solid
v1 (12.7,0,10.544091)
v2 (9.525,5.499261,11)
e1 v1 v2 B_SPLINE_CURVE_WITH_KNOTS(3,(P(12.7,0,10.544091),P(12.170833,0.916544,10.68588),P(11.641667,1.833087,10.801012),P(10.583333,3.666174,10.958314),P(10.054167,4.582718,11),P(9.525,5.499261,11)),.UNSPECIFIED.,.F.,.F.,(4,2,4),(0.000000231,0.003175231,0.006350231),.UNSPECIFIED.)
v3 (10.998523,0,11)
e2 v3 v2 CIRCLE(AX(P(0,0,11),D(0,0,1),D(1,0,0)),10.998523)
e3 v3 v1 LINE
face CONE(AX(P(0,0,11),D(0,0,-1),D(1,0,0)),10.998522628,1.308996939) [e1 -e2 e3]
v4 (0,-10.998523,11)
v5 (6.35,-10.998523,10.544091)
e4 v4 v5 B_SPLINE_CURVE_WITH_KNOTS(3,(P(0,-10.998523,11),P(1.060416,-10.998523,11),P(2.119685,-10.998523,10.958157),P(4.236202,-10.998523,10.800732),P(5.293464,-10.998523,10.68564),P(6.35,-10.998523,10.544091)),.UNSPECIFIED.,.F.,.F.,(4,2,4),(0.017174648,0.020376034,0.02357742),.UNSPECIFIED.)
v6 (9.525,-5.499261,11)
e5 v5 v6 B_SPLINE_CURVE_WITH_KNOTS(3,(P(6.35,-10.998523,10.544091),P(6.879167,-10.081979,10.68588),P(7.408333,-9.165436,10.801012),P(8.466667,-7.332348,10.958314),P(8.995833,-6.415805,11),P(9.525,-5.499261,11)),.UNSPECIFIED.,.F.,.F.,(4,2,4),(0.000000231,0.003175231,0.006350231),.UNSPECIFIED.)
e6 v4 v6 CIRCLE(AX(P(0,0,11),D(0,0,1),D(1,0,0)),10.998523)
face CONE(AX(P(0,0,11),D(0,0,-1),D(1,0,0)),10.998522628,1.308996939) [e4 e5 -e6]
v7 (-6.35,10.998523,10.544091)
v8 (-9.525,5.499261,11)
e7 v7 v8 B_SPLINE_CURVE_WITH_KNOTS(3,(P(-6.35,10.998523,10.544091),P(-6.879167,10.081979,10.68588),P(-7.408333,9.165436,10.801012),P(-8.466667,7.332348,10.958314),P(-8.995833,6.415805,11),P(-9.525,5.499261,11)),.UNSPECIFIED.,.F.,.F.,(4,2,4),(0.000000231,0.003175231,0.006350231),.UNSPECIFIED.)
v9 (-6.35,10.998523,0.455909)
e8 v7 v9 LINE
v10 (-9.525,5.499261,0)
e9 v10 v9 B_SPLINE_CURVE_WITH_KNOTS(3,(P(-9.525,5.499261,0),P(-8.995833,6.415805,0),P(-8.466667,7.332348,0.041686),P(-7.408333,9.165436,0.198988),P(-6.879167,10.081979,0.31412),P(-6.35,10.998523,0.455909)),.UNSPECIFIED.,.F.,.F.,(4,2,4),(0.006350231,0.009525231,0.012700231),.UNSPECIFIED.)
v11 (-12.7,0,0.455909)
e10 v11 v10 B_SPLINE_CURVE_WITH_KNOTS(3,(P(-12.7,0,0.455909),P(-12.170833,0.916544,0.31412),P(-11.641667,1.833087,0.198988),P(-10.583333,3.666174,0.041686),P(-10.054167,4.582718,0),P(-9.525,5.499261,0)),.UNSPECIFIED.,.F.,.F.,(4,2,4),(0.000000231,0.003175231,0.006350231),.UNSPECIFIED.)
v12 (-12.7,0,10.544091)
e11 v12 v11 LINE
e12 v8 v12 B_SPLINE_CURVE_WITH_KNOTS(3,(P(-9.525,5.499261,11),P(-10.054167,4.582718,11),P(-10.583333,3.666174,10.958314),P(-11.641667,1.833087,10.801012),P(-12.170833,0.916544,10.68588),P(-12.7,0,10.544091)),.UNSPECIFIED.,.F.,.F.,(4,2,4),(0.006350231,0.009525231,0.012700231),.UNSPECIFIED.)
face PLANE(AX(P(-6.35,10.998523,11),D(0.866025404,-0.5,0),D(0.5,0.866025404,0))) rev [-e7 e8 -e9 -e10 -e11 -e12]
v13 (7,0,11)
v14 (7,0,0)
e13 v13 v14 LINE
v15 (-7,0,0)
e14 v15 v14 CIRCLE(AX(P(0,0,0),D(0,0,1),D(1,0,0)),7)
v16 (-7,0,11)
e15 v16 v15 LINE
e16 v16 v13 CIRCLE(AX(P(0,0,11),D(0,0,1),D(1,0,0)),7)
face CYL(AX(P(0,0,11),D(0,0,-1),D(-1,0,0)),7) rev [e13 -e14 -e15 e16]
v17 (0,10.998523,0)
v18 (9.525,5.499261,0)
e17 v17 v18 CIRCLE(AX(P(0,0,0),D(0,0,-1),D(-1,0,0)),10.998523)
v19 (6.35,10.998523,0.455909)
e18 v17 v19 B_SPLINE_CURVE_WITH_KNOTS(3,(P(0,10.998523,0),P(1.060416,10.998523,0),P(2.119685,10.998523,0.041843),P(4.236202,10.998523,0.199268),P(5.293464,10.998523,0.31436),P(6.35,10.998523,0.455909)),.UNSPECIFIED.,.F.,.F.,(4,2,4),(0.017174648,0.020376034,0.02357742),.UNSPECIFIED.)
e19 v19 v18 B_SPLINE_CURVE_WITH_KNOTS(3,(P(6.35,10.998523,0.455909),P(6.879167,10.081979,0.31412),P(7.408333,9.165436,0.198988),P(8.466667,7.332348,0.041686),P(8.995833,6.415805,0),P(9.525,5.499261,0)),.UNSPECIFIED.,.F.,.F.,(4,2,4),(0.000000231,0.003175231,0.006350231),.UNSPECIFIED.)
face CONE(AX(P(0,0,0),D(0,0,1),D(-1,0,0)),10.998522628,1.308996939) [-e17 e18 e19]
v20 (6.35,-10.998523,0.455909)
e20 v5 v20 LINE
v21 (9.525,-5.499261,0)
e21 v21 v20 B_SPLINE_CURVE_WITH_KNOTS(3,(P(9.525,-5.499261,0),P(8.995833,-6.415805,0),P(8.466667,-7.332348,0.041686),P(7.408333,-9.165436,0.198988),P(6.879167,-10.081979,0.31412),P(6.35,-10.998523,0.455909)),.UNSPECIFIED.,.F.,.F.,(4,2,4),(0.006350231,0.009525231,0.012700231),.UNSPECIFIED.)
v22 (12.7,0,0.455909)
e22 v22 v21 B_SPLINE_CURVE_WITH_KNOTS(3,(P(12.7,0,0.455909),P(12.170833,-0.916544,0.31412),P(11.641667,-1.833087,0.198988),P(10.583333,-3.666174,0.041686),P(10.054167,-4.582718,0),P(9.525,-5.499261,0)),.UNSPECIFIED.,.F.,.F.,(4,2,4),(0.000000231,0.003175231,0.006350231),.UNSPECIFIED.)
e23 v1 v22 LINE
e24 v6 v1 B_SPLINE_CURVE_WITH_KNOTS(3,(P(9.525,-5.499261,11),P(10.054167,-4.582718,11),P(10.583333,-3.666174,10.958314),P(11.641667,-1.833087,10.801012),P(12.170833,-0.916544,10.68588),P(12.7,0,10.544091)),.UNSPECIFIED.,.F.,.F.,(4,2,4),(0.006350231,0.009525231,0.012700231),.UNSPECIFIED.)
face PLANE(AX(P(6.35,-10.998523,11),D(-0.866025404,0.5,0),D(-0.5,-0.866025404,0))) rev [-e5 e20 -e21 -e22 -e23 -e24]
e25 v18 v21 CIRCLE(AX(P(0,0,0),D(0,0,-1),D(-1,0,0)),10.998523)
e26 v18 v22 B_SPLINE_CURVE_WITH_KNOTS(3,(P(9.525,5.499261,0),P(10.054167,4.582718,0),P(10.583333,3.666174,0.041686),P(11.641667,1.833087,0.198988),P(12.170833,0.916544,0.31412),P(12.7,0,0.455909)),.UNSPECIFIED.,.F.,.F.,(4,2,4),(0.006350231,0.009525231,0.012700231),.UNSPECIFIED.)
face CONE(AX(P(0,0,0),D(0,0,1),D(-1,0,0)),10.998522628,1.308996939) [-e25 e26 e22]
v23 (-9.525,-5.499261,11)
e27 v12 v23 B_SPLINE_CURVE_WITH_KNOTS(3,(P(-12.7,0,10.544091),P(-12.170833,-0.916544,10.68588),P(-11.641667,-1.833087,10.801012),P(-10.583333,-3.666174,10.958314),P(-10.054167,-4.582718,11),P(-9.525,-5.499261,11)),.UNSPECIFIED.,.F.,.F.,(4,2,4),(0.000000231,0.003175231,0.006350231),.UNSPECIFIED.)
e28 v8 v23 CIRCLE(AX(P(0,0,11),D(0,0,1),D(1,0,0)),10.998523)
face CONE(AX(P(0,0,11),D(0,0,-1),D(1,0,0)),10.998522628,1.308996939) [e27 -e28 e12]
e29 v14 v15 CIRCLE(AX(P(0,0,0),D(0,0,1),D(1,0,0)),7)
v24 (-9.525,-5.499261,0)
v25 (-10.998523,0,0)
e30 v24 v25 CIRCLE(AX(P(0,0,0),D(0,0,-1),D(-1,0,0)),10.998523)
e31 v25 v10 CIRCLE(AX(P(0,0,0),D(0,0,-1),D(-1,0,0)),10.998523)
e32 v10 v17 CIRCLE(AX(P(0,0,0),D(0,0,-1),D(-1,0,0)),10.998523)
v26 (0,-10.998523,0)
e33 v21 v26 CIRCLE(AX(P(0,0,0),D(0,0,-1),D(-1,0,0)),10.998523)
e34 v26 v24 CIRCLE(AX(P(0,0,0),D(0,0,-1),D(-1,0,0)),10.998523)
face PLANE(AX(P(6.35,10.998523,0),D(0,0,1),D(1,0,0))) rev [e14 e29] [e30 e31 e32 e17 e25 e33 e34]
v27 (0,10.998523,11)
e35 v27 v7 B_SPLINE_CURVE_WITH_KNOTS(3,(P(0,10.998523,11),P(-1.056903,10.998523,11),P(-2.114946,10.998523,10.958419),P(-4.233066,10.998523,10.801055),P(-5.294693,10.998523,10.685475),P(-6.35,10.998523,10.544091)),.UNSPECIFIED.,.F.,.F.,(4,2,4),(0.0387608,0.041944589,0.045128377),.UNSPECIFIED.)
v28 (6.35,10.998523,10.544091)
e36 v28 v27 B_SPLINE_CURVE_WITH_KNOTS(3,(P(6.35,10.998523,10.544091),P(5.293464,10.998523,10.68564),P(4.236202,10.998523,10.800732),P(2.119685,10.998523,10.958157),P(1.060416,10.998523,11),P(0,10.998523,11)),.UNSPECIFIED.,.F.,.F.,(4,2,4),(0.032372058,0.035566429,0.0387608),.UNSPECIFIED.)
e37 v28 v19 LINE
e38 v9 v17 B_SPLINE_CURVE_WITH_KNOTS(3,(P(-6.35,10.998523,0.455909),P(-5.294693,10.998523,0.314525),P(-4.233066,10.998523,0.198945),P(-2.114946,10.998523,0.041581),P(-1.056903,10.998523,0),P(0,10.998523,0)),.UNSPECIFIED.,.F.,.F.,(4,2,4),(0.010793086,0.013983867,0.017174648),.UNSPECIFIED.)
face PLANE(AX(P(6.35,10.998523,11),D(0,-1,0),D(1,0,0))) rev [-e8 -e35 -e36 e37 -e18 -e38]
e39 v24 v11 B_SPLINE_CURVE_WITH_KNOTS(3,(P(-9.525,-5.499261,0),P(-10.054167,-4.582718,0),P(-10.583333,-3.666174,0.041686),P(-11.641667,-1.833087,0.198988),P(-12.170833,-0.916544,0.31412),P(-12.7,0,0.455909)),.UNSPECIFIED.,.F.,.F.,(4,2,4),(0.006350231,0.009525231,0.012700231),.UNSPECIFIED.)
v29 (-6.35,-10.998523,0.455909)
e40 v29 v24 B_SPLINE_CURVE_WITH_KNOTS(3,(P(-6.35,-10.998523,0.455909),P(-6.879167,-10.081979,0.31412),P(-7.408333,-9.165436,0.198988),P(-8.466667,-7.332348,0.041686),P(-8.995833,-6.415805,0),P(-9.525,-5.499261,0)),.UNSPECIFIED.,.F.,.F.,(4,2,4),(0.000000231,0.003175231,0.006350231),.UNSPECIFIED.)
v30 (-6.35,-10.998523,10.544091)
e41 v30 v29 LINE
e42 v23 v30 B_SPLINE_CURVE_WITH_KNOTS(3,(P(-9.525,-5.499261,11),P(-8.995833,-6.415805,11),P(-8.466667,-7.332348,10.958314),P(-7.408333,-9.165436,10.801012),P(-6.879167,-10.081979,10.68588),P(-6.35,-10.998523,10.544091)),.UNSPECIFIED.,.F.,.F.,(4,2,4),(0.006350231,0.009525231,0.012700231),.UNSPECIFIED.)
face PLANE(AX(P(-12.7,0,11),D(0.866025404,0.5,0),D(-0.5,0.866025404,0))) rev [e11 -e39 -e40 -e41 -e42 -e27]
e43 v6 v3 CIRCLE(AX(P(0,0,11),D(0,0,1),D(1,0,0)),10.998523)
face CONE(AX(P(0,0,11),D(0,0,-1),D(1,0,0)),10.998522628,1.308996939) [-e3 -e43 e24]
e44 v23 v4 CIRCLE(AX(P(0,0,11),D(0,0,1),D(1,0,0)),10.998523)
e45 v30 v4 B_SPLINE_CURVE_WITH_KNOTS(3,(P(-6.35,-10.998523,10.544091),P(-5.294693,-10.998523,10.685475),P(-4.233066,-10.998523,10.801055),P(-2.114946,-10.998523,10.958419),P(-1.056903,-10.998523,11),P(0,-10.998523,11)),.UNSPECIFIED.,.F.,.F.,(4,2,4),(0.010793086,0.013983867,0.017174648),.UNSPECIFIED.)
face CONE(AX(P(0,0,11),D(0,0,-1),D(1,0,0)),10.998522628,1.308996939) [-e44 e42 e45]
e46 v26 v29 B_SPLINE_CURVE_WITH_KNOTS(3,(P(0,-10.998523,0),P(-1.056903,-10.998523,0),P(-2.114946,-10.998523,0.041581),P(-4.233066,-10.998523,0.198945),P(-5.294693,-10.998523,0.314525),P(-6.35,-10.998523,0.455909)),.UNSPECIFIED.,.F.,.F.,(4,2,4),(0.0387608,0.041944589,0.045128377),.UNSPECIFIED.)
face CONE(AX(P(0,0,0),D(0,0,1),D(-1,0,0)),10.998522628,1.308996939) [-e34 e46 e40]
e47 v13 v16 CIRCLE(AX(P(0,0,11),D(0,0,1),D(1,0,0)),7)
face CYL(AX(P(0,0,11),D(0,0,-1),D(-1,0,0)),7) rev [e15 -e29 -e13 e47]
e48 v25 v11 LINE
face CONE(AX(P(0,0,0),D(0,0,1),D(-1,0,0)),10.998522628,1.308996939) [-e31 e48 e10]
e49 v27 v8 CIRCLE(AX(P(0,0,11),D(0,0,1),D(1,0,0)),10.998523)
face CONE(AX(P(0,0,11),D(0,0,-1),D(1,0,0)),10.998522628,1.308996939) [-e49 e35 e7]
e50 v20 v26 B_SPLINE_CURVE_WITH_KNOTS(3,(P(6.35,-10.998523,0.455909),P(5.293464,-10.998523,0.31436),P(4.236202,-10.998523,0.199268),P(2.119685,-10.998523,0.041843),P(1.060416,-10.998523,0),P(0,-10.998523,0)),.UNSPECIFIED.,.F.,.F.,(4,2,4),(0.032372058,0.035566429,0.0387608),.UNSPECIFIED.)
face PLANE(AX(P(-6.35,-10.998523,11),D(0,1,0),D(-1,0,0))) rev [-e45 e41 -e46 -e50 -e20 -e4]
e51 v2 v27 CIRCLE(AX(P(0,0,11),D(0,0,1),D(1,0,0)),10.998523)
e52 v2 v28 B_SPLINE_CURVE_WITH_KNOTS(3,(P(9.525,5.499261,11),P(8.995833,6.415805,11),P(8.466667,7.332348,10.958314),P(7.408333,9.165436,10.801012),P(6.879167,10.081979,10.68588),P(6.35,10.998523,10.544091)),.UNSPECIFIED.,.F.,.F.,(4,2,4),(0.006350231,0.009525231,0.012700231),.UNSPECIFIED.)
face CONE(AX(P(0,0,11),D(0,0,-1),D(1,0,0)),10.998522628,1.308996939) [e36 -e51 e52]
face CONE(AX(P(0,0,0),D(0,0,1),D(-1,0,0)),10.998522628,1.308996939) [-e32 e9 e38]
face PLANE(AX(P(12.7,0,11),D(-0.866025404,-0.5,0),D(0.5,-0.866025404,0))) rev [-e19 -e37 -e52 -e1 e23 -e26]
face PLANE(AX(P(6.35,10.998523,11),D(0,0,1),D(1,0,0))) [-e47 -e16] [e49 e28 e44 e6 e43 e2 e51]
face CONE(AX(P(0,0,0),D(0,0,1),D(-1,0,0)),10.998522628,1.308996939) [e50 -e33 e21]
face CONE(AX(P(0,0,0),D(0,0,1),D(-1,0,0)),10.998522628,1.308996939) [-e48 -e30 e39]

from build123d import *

# Parameters (mm, degrees)
SKETCH1_R          = 7
BASE_EXTRUDE_DEPTH = 11
SKETCH2_OUTSIDE_W  = 318.108
SKETCH2_OUTSIDE_H  = 314.706
SKETCH2_OUTSIDE_R  = 10.998522628
CUT_EXTRUDE1_DEPTH = 38
CUT_EXTRUDE1_DRAFT = -75
SKETCH3_OUTSIDE_W  = 318.108
SKETCH3_OUTSIDE_H  = 314.706
SKETCH3_OUTSIDE_R  = 10.998522628
CUT_EXTRUDE2_DEPTH = 38
CUT_EXTRUDE2_DRAFT = -75


with BuildPart() as part:
    # Sketch1 → Base-Extrude (new body)
    with BuildSketch(Plane.XY):
        Polygon((6.35, 10.998522628), (-6.35, 10.998522628), (-12.7, 0), (-6.35, -10.998522628), (6.35, -10.998522628), (12.7, 0), align=None)
        Circle(SKETCH1_R, mode=Mode.SUBTRACT)
    extrude(amount=BASE_EXTRUDE_DEPTH)


with BuildPart() as cut_extrude1_tool:
    # Sketch2 outside → Cut-Extrude1 (with draft: the straight prism first)
    with BuildSketch(Plane(origin=(0, 0, 0), x_dir=(-1, 0, 0), z_dir=(0, 0, -1))):
        Rectangle(SKETCH2_OUTSIDE_W, SKETCH2_OUTSIDE_H)
        Circle(SKETCH2_OUTSIDE_R, mode=Mode.SUBTRACT)
    extrude(amount=-CUT_EXTRUDE1_DEPTH)
    # Cut-Extrude1: the draft: its side faces are tilted about the plane it starts from
    cut_extrude1_sides = [cut_extrude1_tool.faces().sort_by_distance(p)[0] for p in [
        (0, -157.353, 19),
        (-159.054, 0, 19),
        (0, 157.353, 19),
        (159.054, 0, 19),
        (10.998522628, 0, 19),
    ]]
    draft(cut_extrude1_sides, Plane(origin=(0, 0, 0), x_dir=(-1, 0, 0), z_dir=(0, 0, -1)), CUT_EXTRUDE1_DRAFT)


with BuildPart() as part_1:
    add(part.part)

    # Cut-Extrude1: cut by cut_extrude1_tool
    add(cut_extrude1_tool.part, mode=Mode.SUBTRACT)


with BuildPart() as cut_extrude2_tool:
    # Sketch3 outside → Cut-Extrude2 (with draft: the straight prism first)
    with BuildSketch(Plane.XY.offset(11)):
        Rectangle(SKETCH3_OUTSIDE_W, SKETCH3_OUTSIDE_H)
        Circle(SKETCH3_OUTSIDE_R, mode=Mode.SUBTRACT)
    extrude(amount=-CUT_EXTRUDE2_DEPTH)
    # Cut-Extrude2: the draft: its side faces are tilted about the plane it starts from
    cut_extrude2_sides = [cut_extrude2_tool.faces().sort_by_distance(p)[0] for p in [
        (0, -157.353, -8),
        (159.054, 0, -8),
        (0, 157.353, -8),
        (-159.054, 0, -8),
        (-10.998522628, 0, -8),
    ]]
    draft(cut_extrude2_sides, Plane.XY.offset(11), CUT_EXTRUDE2_DRAFT)


with BuildPart() as part_2:
    add(part_1.part)

    # Cut-Extrude2: cut by cut_extrude2_tool
    add(cut_extrude2_tool.part, mode=Mode.SUBTRACT)


solid = part_2.part
